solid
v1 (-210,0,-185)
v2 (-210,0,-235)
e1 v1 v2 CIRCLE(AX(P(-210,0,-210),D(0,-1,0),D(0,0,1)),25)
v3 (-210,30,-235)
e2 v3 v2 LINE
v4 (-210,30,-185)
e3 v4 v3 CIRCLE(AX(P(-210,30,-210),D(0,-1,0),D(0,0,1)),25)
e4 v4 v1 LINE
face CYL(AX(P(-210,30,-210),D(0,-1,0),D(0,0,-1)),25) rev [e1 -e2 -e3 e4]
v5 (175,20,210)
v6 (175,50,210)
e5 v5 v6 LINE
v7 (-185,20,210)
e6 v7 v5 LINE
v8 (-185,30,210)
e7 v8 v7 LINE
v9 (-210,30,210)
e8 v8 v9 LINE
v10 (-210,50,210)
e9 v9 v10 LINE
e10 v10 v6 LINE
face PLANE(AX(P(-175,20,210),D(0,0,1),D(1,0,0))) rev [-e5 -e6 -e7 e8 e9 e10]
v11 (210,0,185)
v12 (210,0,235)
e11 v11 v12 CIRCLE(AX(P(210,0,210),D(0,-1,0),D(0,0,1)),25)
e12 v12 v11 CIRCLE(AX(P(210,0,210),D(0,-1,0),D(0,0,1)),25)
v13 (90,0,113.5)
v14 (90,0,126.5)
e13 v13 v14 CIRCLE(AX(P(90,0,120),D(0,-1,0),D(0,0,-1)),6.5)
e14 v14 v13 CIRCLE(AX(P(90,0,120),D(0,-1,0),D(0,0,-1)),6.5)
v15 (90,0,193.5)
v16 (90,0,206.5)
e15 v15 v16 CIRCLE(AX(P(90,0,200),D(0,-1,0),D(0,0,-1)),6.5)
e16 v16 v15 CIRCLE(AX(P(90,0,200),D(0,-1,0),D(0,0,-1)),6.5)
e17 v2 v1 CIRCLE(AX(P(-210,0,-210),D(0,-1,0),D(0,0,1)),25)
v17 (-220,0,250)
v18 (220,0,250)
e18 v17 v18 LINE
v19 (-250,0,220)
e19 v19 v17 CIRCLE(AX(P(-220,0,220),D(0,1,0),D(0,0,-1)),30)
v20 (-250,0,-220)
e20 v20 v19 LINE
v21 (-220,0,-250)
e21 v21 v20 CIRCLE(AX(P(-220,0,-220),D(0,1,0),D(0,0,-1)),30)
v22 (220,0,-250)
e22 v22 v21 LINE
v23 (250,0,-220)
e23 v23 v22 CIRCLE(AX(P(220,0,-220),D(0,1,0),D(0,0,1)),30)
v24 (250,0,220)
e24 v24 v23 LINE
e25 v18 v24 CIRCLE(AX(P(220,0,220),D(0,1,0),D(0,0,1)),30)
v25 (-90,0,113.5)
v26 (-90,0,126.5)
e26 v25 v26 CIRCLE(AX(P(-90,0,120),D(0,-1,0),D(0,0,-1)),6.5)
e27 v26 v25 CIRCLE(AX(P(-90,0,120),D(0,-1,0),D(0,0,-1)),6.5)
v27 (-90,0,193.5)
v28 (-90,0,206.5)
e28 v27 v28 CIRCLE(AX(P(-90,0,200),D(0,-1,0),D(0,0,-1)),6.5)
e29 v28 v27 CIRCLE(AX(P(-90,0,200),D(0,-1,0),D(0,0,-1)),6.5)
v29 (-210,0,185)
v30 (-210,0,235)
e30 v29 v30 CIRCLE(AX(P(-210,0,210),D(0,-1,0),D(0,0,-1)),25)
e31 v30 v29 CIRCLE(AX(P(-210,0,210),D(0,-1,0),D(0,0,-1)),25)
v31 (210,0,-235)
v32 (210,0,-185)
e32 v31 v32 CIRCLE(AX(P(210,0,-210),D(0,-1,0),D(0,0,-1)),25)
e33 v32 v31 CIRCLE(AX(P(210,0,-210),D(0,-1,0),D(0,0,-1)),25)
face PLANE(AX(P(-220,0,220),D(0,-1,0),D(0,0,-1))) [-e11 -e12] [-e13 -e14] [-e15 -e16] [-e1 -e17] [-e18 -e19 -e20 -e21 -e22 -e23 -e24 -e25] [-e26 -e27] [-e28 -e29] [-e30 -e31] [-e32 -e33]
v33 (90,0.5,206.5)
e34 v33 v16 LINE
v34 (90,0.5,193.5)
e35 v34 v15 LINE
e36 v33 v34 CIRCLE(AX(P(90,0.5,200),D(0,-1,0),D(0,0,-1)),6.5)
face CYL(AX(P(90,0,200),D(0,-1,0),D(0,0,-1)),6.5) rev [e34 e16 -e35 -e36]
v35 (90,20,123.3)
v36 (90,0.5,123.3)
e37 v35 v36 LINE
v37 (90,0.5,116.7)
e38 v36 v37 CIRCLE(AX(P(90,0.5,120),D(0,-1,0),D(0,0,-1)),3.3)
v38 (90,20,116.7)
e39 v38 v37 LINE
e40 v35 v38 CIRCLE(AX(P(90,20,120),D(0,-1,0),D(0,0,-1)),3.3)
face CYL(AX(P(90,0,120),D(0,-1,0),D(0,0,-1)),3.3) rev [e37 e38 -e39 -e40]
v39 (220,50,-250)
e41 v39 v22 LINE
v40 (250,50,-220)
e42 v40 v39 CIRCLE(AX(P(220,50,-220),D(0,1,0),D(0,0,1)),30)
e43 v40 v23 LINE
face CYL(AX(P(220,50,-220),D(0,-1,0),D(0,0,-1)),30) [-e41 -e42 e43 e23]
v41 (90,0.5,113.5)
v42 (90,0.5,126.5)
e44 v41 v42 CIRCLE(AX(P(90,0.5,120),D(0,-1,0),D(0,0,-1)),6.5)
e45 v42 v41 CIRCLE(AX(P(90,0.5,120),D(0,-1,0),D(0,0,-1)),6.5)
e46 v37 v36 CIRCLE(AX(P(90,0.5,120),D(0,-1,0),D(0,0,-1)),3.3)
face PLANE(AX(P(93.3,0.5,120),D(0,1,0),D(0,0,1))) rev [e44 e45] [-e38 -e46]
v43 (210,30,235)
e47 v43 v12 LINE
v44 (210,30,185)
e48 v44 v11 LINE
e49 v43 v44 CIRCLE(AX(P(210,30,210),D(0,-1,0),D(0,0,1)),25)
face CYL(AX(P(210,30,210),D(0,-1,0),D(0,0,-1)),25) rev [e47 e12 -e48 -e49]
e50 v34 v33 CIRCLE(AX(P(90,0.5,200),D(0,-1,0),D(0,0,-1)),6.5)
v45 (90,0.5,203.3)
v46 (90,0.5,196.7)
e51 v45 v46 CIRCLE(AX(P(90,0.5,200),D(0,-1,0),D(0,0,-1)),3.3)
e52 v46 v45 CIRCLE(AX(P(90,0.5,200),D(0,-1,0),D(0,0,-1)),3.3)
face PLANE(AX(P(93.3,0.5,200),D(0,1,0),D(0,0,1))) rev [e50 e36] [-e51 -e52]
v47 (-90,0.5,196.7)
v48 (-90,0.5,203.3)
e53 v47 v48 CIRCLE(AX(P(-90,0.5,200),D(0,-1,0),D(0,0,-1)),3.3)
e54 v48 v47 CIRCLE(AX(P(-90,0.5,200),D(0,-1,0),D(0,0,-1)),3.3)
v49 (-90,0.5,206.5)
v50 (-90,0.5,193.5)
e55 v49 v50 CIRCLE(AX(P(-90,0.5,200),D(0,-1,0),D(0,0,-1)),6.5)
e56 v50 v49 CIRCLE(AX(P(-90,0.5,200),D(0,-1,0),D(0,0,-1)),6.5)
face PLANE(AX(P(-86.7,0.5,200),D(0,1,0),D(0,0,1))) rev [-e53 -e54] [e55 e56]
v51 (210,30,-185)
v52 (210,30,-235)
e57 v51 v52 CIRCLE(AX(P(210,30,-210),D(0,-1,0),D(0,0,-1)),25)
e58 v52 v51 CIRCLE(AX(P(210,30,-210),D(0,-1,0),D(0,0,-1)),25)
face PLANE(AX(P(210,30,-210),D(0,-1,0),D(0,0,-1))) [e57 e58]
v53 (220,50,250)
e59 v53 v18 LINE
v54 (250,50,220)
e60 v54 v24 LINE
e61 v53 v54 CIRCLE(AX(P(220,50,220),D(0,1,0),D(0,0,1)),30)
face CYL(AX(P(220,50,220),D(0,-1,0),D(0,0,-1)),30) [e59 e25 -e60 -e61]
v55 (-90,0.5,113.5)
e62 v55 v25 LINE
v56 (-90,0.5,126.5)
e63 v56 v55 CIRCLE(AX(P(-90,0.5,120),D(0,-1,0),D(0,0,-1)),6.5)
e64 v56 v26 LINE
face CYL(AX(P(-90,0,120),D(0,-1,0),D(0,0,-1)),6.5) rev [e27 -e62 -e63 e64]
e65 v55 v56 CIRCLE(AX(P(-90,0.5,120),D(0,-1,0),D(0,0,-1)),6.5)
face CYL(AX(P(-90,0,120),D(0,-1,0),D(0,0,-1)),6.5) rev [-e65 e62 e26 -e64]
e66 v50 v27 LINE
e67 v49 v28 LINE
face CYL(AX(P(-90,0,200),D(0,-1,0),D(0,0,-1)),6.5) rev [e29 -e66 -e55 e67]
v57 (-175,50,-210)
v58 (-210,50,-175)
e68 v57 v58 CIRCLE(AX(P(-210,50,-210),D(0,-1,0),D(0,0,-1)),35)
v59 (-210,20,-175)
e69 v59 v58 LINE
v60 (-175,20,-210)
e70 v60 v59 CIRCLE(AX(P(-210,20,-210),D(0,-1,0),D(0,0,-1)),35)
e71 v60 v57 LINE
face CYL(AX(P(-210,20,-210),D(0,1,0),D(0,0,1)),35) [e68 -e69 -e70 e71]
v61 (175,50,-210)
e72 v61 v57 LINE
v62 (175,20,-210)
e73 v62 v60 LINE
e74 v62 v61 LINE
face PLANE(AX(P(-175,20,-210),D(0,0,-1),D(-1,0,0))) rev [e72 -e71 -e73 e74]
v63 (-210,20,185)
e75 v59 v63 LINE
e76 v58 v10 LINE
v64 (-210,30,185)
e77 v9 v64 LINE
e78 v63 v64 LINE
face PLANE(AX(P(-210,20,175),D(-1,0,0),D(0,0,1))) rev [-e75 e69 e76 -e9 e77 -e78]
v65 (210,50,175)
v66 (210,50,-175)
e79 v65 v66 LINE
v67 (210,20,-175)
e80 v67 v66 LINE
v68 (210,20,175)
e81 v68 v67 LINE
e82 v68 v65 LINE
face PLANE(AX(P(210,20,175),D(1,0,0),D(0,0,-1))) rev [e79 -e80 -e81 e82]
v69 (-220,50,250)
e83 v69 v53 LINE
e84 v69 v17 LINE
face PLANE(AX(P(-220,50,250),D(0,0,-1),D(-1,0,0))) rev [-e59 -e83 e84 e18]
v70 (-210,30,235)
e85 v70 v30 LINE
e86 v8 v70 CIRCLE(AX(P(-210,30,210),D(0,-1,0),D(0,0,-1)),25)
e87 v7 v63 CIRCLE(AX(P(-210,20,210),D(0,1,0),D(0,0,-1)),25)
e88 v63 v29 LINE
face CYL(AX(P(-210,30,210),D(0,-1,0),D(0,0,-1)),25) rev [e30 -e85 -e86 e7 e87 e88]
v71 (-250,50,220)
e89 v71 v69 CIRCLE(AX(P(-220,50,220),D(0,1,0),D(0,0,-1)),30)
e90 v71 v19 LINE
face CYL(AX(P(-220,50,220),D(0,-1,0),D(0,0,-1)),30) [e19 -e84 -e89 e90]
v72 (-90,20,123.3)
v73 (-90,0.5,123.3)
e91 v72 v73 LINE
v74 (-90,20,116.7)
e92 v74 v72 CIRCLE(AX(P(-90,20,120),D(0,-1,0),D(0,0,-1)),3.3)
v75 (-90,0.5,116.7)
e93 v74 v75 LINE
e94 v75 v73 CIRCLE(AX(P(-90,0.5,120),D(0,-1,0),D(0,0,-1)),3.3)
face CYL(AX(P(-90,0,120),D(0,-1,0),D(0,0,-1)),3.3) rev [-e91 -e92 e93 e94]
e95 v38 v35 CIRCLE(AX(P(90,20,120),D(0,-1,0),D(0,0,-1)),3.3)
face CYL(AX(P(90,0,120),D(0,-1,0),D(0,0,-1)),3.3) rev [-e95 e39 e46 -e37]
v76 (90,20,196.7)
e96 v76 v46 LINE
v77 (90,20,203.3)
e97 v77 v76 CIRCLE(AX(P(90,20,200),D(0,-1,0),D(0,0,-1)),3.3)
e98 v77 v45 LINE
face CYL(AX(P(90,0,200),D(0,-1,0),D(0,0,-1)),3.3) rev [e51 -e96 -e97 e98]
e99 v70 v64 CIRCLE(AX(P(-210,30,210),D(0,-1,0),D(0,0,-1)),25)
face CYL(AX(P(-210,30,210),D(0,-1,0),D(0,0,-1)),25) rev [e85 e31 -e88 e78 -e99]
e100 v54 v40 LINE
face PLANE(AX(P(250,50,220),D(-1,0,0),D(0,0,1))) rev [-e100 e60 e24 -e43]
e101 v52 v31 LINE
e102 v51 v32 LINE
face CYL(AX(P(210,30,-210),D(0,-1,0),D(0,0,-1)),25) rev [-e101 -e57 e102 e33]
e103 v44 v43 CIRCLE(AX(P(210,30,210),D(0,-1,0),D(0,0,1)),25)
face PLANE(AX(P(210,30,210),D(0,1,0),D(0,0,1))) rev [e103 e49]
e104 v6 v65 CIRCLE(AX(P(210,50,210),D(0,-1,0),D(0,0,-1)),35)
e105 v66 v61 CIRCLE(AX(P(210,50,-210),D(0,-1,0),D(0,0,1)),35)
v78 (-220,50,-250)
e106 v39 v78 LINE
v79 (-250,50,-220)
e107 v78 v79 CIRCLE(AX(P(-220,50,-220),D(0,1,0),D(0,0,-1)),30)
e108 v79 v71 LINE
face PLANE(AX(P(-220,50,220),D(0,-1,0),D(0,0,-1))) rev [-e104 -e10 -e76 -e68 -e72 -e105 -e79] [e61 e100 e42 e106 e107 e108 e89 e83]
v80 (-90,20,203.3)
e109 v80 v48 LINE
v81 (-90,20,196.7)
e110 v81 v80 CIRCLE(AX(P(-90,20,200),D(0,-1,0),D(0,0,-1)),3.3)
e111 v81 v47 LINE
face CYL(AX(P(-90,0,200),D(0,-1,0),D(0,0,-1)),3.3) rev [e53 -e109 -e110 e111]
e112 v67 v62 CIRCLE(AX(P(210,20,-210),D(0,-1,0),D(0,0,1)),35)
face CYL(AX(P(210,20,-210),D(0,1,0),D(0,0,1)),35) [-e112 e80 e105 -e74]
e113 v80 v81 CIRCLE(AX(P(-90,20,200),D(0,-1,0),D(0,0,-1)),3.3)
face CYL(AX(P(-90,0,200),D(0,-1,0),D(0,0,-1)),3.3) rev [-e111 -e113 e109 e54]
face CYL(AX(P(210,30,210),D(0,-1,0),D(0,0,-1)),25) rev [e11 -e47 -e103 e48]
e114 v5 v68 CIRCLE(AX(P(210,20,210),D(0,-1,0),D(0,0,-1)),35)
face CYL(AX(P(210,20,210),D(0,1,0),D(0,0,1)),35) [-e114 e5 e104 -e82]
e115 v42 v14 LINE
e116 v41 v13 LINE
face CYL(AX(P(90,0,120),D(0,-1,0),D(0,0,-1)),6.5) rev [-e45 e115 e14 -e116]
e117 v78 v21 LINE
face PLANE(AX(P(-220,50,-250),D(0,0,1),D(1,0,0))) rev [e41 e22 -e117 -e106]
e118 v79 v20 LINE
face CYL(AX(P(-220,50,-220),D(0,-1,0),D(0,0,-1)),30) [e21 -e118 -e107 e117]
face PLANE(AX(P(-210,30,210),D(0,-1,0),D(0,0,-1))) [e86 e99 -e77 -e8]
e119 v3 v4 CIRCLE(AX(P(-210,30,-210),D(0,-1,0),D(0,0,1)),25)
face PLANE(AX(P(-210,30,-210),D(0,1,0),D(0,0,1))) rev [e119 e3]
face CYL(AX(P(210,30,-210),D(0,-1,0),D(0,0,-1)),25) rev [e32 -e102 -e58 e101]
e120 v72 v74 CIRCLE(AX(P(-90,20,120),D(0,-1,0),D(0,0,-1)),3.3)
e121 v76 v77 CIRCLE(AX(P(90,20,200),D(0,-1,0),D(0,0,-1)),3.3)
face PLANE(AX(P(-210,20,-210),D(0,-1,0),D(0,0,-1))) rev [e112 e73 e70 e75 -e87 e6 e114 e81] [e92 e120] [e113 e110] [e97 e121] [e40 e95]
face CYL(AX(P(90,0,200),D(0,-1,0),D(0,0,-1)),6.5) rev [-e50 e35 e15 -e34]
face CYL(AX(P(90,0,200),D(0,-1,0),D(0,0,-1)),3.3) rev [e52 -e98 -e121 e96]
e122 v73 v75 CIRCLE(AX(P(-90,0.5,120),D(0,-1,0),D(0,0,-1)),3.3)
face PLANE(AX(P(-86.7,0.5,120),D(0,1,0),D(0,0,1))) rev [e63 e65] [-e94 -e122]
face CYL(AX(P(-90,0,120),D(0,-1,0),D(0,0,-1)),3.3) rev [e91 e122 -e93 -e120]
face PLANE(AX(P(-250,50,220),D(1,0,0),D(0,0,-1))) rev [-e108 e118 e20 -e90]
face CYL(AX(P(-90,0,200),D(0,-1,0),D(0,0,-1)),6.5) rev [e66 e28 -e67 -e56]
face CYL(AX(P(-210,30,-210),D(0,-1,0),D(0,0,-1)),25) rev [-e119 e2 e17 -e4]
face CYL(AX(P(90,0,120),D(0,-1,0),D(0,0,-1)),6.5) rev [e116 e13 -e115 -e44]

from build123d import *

# Parameters (mm, degrees)
BOSS_EXTRUDE1_DEPTH                                  = 50
CUT_EXTRUDE1_DEPTH                                   = 30
SKETCH3_R                                            = 25
CUT_EXTRUDE2_DEPTH                                   = 30
CBORE_FOR_M6_HEXAGON_HEAD_BOLTS_FULL_THR_D           = 6.6
CBORE_FOR_M6_HEXAGON_HEAD_BOLTS_FULL_THR_CBORE_D     = 13
CBORE_FOR_M6_HEXAGON_HEAD_BOLTS_FULL_THR_CBORE_DEPTH = 0.5
CUT_EXTRUDE8_DEPTH                                   = 30


with BuildPart() as part:
    # Sketch1 → Boss-Extrude1 (new body)
    with BuildSketch(Plane(origin=(0, 0, 0), x_dir=(1, 0, 0), z_dir=(0, 1, 0))):
        with BuildLine():
            Line((-220, -250), (220, -250))
            ThreePointArc((220, -250), (241.213203436, -241.213203436), (250, -220))
            Line((250, -220), (250, 220))
            ThreePointArc((250, 220), (241.213203436, 241.213203436), (220, 250))
            Line((220, 250), (-220, 250))
            ThreePointArc((-220, 250), (-241.213203436, 241.213203436), (-250, 220))
            Line((-250, 220), (-250, -220))
            ThreePointArc((-250, -220), (-241.213203436, -241.213203436), (-220, -250))
        make_face()
    extrude(amount=BOSS_EXTRUDE1_DEPTH)

    # Sketch2 → Cut-Extrude1 (cut)
    with BuildSketch(Plane(origin=(0, 50, 0), x_dir=(1, 0, 0), z_dir=(0, 1, 0))):
        with BuildLine():
            Line((-175, -210), (175, -210))
            ThreePointArc((175, -210), (185.251262658, -185.251262658), (210, -175))
            Line((210, -175), (210, 175))
            ThreePointArc((210, 175), (185.251262658, 185.251262658), (175, 210))
            Line((175, 210), (-175, 210))
            ThreePointArc((-175, 210), (-185.251262658, 185.251262658), (-210, 175))
            Line((-210, 175), (-210, -175))
            ThreePointArc((-210, -175), (-185.251262658, -185.251262658), (-175, -210))
        make_face()
    extrude(amount=-CUT_EXTRUDE1_DEPTH, mode=Mode.SUBTRACT)

    # Sketch3 → Cut-Extrude2 (cut)
    with BuildSketch(Plane.XZ):
        with Locations(Location((-210, 210, 0), (0, 0, 270))):
            Circle(SKETCH3_R)
        with Locations(Location((210, 210, 0), (0, 0, 90))):
            Circle(SKETCH3_R)
        with Locations(Location((210, -210, 0), (0, 0, 270))):
            Circle(SKETCH3_R)
        with Locations(Location((-210, -210, 0), (0, 0, 90))):
            Circle(SKETCH3_R)
    extrude(amount=-CUT_EXTRUDE2_DEPTH, mode=Mode.SUBTRACT)

    # CBORE for M6 Hexagon head bolts-Full thread-grade C1 (through all)
    with Locations(Plane.XZ):
        with Locations((90, 200), (-90, 200), (90, 120), (-90, 120)):
            CounterBoreHole(CBORE_FOR_M6_HEXAGON_HEAD_BOLTS_FULL_THR_D / 2, CBORE_FOR_M6_HEXAGON_HEAD_BOLTS_FULL_THR_CBORE_D / 2, CBORE_FOR_M6_HEXAGON_HEAD_BOLTS_FULL_THR_CBORE_DEPTH)

    # Sketch10 → Cut-Extrude8 (cut)
    with BuildSketch(Plane(origin=(0, 50, 0), x_dir=(1, 0, 0), z_dir=(0, 1, 0))):
        with BuildLine():
            Line((-210, -175), (-210, -210))
            Line((-210, -210), (-175, -210))
            ThreePointArc((-175, -210), (-185.251262658, -185.251262658), (-210, -175))
        make_face()
    extrude(amount=-CUT_EXTRUDE8_DEPTH, mode=Mode.SUBTRACT)


solid = part.part
